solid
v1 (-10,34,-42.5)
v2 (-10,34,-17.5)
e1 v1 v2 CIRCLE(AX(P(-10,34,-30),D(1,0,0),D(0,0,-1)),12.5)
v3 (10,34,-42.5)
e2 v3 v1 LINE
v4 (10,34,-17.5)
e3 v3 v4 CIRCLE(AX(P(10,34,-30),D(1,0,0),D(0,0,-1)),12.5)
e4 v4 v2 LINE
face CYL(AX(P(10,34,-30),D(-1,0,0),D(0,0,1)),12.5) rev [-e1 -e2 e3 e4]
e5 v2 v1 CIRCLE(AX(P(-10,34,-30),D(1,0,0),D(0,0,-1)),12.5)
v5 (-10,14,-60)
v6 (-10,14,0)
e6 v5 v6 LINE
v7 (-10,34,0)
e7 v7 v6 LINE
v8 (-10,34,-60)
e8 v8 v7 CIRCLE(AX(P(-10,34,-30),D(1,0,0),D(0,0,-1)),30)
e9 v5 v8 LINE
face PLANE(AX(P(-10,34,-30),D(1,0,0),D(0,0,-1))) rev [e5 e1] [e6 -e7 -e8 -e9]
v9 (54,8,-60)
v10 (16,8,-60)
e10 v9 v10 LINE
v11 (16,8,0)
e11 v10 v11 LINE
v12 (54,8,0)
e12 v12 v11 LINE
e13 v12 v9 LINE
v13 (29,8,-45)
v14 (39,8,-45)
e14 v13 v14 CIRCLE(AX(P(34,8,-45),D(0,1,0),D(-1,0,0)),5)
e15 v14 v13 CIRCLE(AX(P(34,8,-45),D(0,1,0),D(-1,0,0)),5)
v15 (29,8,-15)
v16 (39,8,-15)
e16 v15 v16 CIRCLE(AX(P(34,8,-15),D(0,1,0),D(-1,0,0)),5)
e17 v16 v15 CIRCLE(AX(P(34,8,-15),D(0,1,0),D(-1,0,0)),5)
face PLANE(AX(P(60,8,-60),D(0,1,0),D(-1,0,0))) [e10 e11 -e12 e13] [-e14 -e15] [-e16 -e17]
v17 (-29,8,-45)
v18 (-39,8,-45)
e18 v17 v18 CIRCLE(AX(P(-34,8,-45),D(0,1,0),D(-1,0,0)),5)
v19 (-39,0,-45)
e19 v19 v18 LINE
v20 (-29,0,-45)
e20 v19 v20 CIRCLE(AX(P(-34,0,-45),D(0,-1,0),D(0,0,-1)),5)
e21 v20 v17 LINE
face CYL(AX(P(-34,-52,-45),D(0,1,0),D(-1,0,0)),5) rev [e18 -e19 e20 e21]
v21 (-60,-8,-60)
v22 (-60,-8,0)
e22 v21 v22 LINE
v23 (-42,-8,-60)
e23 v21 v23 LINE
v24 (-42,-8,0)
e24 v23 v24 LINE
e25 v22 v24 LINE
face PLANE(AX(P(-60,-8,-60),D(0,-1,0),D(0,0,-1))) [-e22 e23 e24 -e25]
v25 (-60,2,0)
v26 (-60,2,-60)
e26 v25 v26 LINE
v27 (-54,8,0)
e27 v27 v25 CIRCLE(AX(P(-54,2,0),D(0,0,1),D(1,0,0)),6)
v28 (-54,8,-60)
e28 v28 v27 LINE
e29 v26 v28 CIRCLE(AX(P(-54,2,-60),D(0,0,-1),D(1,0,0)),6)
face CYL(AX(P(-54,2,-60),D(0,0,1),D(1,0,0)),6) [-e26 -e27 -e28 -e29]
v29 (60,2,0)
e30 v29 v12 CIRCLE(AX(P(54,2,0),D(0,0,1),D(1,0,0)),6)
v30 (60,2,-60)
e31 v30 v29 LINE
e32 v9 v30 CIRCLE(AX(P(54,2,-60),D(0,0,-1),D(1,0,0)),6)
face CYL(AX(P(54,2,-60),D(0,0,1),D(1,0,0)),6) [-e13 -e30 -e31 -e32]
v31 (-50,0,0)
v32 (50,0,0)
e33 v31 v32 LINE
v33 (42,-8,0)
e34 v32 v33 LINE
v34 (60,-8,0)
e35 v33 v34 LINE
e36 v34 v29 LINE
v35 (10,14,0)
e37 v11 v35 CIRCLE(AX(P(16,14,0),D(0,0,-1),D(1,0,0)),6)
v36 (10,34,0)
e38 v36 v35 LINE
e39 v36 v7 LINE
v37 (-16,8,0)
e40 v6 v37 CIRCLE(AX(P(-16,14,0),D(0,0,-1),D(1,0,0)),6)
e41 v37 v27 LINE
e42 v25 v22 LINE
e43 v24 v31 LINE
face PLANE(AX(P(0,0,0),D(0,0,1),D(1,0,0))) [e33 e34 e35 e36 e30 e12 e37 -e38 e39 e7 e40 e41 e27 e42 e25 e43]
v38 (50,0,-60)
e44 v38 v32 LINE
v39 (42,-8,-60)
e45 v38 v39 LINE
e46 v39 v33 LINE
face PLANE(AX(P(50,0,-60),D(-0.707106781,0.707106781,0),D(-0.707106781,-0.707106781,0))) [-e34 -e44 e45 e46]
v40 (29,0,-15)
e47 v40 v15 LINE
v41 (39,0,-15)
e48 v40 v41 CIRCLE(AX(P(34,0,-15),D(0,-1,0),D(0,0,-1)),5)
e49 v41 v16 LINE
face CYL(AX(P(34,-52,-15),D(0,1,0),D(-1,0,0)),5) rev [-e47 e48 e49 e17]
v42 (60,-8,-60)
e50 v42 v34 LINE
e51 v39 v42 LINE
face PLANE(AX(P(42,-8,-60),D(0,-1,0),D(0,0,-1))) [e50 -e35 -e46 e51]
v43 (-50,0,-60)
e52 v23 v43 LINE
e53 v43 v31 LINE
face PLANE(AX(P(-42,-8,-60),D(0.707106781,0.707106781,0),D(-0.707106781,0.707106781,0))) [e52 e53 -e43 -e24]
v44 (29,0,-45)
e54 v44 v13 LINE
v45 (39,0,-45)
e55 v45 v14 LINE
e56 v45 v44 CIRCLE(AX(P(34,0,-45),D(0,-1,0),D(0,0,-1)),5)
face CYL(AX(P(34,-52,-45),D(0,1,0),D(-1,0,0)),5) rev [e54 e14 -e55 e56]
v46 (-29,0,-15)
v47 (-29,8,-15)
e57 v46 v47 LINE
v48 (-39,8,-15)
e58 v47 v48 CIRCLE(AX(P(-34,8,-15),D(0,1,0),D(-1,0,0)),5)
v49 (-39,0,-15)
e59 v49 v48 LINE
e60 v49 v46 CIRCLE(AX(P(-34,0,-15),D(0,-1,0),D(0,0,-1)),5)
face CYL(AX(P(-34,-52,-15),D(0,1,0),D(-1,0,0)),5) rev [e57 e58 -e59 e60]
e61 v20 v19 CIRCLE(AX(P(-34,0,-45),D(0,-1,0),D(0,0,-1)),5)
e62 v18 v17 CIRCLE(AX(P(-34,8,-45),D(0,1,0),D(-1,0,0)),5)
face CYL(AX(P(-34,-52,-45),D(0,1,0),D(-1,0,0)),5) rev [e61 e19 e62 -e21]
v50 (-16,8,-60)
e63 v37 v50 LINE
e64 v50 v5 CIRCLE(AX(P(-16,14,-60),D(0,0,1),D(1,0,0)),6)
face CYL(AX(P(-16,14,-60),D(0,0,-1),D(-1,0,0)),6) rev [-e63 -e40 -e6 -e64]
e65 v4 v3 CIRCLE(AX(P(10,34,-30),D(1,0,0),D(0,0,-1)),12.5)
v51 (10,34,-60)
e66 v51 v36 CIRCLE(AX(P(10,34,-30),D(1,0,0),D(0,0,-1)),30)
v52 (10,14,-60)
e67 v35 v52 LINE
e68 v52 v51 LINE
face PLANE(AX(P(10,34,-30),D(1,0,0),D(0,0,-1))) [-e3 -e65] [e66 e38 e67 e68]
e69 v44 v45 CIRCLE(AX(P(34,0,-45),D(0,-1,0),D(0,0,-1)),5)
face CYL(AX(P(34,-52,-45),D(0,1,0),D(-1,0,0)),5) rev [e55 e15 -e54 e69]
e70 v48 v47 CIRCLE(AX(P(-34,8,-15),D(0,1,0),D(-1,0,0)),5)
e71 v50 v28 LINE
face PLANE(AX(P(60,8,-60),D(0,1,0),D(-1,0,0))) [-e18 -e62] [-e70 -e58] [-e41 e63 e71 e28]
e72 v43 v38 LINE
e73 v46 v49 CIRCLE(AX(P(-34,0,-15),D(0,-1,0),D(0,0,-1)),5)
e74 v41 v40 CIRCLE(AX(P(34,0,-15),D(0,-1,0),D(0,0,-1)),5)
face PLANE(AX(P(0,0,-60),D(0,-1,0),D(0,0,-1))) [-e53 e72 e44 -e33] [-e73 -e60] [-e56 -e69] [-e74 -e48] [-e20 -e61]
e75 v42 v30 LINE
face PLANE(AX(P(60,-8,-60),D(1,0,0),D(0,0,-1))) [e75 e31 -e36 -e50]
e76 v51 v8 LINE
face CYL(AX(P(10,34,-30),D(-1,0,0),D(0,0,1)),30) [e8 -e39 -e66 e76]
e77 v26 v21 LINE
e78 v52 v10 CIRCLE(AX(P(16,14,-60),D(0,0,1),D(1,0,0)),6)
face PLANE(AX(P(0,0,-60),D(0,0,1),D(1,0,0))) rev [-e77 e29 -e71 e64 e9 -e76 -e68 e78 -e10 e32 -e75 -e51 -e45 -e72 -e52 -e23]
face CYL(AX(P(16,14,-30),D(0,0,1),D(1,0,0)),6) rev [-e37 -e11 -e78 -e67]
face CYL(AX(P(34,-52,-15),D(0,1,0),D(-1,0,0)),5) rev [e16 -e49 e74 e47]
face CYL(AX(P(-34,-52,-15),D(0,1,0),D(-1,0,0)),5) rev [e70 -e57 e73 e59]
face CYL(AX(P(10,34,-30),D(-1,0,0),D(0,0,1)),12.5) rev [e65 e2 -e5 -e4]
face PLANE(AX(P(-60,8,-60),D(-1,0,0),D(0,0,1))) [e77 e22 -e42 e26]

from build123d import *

# Parameters (mm, degrees)
BASE_PLATE_DEPTH         = 60
MOUNTING_HOLES_SKETCH_R  = 5
MOUNTING_HOLES_DEPTH     = 60
EYE_UPRIGHT_PROFILE_R    = 12.5
EYE_UPRIGHT_DEPTH        = 10
UPRIGHT_ROOT_FILLET_R6_R = 6


with BuildPart() as part:
    # Base Plate Profile → Base Plate (new body)
    with BuildSketch(Plane.XY):
        Polygon((0, 0), (50, 0), (42, -8), (60, -8), (60, 8), (-60, 8), (-60, -8), (-42, -8), (-50, 0), align=None)
    extrude(amount=-BASE_PLATE_DEPTH)

    # Mounting Holes Sketch → Mounting Holes (cut)
    with BuildSketch(Plane(origin=(0, 8, 0), x_dir=(1, 0, 0), z_dir=(0, 1, 0))):
        with Locations(Location((34, 45, 0), (0, 0, 180))):
            Circle(MOUNTING_HOLES_SKETCH_R)
        with Locations(Location((34, 15, 0), (0, 0, 180))):
            Circle(MOUNTING_HOLES_SKETCH_R)
        with Locations(Location((-34, 45, 0), (0, 0, 180))):
            Circle(MOUNTING_HOLES_SKETCH_R)
        with Locations(Location((-34, 15, 0), (0, 0, 180))):
            Circle(MOUNTING_HOLES_SKETCH_R)
    extrude(amount=-MOUNTING_HOLES_DEPTH, mode=Mode.SUBTRACT)

    # Eye Upright Profile → Eye Upright (add, symmetric)
    with BuildSketch(Plane(origin=(0, 0, 0), x_dir=(0, 0, -1), z_dir=(1, 0, 0))):
        with BuildLine():
            Line((0, 8), (0, 34))
            ThreePointArc((0, 34), (30, 64), (60, 34))
            Line((60, 34), (60, 8))
            Line((60, 8), (0, 8))
        make_face()
        with Locations((30, 34)):
            Circle(EYE_UPRIGHT_PROFILE_R, mode=Mode.SUBTRACT)
    extrude(amount=EYE_UPRIGHT_DEPTH, both=True)

    # Upright Root Fillet R6
    upright_root_fillet_r6_edges = [part.edges().sort_by_distance(p)[0] for p in [
        (-60, 8, -30),
        (60, 8, -30),
        (10, 8, -30),
        (-10, 8, -30),
    ]]
    fillet(upright_root_fillet_r6_edges, radius=UPRIGHT_ROOT_FILLET_R6_R)


solid = part.part
